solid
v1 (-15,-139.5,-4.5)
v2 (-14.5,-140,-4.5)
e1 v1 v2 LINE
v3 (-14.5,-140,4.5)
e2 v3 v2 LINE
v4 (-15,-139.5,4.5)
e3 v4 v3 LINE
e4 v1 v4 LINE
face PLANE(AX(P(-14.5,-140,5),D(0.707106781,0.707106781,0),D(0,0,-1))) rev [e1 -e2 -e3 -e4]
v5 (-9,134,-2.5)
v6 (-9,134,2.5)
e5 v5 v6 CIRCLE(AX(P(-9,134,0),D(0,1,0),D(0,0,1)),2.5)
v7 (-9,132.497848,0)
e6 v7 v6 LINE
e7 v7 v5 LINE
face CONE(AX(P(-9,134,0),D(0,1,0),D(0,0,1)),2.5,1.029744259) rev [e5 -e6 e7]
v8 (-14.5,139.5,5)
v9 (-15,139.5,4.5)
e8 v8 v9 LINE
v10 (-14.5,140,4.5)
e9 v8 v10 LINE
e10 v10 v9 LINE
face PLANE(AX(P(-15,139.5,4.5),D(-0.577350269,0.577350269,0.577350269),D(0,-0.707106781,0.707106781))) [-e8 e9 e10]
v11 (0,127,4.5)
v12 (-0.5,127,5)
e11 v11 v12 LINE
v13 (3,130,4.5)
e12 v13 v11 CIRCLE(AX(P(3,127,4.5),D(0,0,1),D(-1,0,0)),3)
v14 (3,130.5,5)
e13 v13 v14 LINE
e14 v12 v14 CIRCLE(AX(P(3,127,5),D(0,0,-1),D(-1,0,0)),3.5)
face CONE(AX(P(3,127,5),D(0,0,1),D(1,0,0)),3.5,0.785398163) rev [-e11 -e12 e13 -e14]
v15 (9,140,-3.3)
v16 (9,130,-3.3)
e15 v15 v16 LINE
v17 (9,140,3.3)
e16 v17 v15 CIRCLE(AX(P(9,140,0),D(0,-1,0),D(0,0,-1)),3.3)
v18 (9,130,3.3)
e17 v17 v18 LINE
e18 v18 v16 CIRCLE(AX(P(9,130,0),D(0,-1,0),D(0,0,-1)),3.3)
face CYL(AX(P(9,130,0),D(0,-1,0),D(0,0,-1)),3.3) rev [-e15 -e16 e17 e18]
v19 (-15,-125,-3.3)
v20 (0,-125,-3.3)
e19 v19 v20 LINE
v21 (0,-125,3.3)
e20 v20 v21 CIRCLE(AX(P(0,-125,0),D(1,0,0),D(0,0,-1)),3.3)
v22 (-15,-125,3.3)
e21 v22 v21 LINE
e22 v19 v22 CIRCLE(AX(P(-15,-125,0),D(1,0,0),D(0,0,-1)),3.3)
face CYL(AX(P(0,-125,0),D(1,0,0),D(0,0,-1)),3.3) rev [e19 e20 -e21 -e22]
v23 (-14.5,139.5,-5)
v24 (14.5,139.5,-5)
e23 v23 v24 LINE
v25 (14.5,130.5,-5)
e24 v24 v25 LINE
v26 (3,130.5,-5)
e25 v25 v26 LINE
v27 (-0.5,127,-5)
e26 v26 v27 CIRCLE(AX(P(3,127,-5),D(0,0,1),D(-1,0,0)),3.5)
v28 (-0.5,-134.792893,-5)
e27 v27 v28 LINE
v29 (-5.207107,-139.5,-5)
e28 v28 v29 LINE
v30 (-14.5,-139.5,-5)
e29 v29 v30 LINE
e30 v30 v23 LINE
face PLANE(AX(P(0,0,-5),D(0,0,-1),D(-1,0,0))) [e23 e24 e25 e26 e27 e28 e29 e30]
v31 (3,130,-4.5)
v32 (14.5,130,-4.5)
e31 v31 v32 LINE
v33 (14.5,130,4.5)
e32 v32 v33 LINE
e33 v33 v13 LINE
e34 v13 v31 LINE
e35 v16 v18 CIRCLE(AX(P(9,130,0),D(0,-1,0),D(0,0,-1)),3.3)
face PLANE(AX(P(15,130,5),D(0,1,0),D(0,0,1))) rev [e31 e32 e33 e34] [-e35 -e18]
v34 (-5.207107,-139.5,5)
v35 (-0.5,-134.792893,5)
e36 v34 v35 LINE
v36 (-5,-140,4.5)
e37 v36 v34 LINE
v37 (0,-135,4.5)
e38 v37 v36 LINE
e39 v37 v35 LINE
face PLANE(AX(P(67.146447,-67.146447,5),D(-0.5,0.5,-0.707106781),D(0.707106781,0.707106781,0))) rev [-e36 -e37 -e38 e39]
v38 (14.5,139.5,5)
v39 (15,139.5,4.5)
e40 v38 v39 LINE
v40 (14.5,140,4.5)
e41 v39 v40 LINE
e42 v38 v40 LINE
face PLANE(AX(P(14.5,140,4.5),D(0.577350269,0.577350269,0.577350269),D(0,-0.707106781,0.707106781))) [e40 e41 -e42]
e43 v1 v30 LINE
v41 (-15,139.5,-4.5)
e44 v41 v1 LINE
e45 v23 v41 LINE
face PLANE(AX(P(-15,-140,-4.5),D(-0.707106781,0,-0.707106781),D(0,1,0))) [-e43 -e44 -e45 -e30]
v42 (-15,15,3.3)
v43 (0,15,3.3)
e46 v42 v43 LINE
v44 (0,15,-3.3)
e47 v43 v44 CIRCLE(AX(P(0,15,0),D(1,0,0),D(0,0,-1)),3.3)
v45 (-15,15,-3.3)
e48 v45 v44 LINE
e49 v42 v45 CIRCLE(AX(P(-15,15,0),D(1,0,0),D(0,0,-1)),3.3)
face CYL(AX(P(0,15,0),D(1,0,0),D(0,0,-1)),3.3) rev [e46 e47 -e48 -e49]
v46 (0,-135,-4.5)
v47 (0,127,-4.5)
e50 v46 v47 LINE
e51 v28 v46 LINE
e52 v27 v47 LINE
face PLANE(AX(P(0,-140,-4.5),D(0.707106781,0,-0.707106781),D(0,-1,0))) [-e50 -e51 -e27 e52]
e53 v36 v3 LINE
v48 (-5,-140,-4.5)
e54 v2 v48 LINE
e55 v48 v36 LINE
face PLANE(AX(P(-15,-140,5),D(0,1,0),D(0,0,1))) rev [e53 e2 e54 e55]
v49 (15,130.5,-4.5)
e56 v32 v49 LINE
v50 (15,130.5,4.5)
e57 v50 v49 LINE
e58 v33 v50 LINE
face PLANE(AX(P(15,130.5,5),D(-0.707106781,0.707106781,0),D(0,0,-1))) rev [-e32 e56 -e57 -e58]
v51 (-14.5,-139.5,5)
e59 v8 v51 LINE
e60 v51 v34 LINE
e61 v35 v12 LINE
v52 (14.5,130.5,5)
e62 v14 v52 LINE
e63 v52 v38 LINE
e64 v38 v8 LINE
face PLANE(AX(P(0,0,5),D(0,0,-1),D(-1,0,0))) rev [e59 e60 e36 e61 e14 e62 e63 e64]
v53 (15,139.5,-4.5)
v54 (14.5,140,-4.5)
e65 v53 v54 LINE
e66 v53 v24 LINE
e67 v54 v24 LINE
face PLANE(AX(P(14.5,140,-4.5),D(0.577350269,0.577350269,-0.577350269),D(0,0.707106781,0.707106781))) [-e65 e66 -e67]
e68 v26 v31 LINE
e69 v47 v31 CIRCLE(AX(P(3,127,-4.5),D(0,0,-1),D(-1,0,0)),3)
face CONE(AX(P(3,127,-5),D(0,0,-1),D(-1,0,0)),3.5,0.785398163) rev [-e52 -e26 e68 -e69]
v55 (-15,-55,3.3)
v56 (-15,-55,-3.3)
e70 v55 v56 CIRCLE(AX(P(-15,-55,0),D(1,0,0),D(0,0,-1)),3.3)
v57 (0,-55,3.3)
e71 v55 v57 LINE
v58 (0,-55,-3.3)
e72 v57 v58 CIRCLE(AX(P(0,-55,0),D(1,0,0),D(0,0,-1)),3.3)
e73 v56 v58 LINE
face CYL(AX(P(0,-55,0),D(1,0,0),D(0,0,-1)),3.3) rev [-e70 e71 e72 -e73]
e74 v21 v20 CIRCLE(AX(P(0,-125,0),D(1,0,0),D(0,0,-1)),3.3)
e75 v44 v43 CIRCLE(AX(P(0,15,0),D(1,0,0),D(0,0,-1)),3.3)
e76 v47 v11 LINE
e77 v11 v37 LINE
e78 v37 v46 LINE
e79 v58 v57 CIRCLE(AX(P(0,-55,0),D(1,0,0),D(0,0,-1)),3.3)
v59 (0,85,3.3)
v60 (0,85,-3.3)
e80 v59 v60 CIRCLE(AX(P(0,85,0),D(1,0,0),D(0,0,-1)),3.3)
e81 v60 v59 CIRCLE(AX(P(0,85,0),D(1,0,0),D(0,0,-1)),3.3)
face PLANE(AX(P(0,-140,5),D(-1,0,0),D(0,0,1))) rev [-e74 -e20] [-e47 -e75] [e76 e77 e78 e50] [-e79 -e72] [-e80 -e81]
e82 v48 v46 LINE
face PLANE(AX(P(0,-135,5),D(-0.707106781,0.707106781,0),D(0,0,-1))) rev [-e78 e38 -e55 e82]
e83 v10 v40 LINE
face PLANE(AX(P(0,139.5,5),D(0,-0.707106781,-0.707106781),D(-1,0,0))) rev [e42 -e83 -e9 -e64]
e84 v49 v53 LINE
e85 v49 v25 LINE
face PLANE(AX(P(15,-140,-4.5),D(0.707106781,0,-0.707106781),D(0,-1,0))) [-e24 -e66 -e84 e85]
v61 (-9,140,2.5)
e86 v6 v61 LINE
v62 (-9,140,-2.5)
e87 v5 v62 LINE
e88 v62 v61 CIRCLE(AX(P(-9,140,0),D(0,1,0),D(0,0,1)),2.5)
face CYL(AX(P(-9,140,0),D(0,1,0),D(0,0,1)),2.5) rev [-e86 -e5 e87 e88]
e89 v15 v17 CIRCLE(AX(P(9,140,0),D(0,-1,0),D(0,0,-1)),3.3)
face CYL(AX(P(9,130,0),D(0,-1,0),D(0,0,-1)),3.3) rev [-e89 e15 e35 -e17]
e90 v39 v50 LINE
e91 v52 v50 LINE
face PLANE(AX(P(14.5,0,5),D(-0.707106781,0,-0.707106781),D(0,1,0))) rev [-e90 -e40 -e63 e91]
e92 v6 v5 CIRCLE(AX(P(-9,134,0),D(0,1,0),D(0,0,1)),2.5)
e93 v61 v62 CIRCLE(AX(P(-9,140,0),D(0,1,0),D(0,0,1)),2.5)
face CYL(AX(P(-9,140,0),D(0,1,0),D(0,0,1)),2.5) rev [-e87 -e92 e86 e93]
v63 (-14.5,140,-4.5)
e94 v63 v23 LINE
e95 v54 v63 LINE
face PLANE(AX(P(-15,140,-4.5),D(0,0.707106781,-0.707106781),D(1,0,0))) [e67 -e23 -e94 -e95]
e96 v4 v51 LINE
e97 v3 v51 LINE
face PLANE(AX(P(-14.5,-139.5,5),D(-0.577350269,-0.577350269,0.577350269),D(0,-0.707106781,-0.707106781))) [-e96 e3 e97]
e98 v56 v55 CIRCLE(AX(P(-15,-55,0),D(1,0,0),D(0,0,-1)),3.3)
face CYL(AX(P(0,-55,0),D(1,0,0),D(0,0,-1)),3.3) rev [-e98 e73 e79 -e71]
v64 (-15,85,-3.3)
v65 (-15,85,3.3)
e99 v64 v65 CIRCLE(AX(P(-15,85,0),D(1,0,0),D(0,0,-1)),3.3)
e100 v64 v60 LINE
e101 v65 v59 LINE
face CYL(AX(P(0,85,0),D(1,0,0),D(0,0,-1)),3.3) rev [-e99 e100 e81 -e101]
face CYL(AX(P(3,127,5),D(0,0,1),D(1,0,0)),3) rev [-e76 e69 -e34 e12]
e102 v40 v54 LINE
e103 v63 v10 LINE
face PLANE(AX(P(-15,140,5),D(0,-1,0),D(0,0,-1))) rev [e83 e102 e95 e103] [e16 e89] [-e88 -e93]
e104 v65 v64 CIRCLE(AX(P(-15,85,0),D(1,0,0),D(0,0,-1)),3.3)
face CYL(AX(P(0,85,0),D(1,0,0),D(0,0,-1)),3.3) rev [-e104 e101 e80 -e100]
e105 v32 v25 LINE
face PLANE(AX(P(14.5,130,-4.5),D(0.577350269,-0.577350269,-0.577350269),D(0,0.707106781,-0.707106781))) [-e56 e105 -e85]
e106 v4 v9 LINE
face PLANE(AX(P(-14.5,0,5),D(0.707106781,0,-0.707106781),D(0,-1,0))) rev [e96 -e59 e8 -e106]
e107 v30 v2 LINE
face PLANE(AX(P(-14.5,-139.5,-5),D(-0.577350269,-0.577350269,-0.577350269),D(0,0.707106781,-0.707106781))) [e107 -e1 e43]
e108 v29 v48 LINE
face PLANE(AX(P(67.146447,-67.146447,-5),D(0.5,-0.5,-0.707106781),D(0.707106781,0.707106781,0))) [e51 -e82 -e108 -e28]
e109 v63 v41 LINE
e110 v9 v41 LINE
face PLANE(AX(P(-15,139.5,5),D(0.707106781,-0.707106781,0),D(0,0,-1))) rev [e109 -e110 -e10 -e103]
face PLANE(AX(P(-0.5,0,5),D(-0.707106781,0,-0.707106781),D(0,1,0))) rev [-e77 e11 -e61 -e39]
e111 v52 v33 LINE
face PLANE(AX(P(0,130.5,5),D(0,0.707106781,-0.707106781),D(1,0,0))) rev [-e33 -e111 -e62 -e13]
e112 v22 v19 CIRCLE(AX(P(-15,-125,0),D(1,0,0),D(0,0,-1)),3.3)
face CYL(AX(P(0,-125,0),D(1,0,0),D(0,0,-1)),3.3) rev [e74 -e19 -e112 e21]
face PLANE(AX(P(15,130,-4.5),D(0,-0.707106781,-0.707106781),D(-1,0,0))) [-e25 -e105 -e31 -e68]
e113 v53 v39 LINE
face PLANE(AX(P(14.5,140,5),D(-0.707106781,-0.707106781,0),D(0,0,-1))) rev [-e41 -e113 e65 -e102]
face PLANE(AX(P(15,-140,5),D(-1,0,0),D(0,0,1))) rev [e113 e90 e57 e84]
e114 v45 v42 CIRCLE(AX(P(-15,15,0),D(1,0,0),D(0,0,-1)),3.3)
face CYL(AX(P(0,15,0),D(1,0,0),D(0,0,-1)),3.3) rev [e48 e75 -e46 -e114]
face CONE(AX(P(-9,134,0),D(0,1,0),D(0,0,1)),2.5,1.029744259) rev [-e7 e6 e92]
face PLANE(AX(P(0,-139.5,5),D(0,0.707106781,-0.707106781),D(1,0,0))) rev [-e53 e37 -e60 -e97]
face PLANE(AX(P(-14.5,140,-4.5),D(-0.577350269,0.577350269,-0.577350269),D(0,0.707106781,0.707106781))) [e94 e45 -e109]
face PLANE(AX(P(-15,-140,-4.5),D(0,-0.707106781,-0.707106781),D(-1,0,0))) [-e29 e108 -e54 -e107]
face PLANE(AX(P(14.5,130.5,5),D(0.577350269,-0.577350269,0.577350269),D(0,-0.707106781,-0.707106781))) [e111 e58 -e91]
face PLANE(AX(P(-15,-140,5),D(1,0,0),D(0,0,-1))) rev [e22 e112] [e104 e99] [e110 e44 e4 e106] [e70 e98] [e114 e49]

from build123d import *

# Parameters (mm, degrees)
SKETCH_1_W          = 30
SKETCH_1_H          = 280
EXTRUDE_1_DEPTH     = 5
SKETCH_2_W          = 15
SKETCH_2_H          = 270
CUT_EXTRUDE_1_DEPTH = 142.155942135
FILLET_1_R          = 3
HOLE_WIZARD_M6_1_D  = 6.6
CHAMFER_1_SIZE      = 5
HOLE_WIZARD_M6_2_D  = 6.6
CHAMFER_2_SIZE      = 0.5
F_5_0MM_1_D         = 5
F_5_0MM_1_DEPTH     = 6
F_5_0MM_1_TIP       = 1.502151548


with BuildPart() as part:
    # 草图1 → 凸台-拉伸1 (new, symmetric)
    with BuildSketch(Plane.XY):
        Rectangle(SKETCH_1_W, SKETCH_1_H)
    extrude(amount=EXTRUDE_1_DEPTH, both=True)

    # 草图2 → 切除-拉伸1 (cut, through all)
    with BuildSketch(Plane(origin=(0, 0, -5), x_dir=(-1, 0, 0), z_dir=(0, 0, -1))):
        with Locations((-7.5, -5)):
            Rectangle(SKETCH_2_W, SKETCH_2_H)
    extrude(amount=-CUT_EXTRUDE_1_DEPTH, mode=Mode.SUBTRACT)

    # 圆角1
    fillet_1_edges = [part.edges().sort_by_distance(p)[0] for p in [
        (0, 130, 0),
    ]]
    fillet(fillet_1_edges, radius=FILLET_1_R)

    # M6 间隙孔1 (through all)
    with Locations(Plane(origin=(0, 130, 0), x_dir=(-1, 0, 0), z_dir=(0, -1, 0))):
        with Locations((-9, 0)):
            Hole(HOLE_WIZARD_M6_1_D / 2)

    # 倒角1
    chamfer_1_edges = [part.edges().sort_by_distance(p)[0] for p in [
        (0, -140, 0),
    ]]
    chamfer(chamfer_1_edges, length=CHAMFER_1_SIZE)

    # M6 间隙孔2 (through all)
    with Locations(Plane(origin=(0, 0, 0), x_dir=(0, 0, -1), z_dir=(1, 0, 0))):
        with Locations((0, 85), (0, 15), (0, -55), (0, -125)):
            Hole(HOLE_WIZARD_M6_2_D / 2)

    # 倒角2
    chamfer_2_edges = [part.edges().sort_by_distance(p)[0] for p in [
        (-15, 0, 5),
        (-10, -140, 5),
        (15, 135, -5),
        (15, 135, 5),
        (15, 130, 0),
        (9, 130, -5),
        (9, 130, 5),
        (0.878679656, 129.121320344, -5),
        (0.878679656, 129.121320344, 5),
        (0, -4, -5),
        (0, -4, 5),
        (-2.5, -137.5, -5),
        (-10, -140, -5),
        (-2.5, -137.5, 5),
        (-15, 0, -5),
        (0, 140, -5),
        (0, 140, 5),
        (-15, -140, 0),
        (-15, 140, 0),
        (15, 140, 0),
    ]]
    chamfer(chamfer_2_edges, length=CHAMFER_2_SIZE)

    # Ø5.0mm 暗销孔1
    with Locations(Plane(origin=(0, 140, 0), x_dir=(1, 0, 0), z_dir=(0, 1, 0))):
        with Locations((-9, 0)):
            Hole(F_5_0MM_1_D / 2, depth=F_5_0MM_1_DEPTH)
            with Locations((0, 0, -(F_5_0MM_1_DEPTH + F_5_0MM_1_TIP / 2))):  # 118° drill point
                Cone(0, F_5_0MM_1_D / 2, F_5_0MM_1_TIP, mode=Mode.SUBTRACT)


solid = part.part
